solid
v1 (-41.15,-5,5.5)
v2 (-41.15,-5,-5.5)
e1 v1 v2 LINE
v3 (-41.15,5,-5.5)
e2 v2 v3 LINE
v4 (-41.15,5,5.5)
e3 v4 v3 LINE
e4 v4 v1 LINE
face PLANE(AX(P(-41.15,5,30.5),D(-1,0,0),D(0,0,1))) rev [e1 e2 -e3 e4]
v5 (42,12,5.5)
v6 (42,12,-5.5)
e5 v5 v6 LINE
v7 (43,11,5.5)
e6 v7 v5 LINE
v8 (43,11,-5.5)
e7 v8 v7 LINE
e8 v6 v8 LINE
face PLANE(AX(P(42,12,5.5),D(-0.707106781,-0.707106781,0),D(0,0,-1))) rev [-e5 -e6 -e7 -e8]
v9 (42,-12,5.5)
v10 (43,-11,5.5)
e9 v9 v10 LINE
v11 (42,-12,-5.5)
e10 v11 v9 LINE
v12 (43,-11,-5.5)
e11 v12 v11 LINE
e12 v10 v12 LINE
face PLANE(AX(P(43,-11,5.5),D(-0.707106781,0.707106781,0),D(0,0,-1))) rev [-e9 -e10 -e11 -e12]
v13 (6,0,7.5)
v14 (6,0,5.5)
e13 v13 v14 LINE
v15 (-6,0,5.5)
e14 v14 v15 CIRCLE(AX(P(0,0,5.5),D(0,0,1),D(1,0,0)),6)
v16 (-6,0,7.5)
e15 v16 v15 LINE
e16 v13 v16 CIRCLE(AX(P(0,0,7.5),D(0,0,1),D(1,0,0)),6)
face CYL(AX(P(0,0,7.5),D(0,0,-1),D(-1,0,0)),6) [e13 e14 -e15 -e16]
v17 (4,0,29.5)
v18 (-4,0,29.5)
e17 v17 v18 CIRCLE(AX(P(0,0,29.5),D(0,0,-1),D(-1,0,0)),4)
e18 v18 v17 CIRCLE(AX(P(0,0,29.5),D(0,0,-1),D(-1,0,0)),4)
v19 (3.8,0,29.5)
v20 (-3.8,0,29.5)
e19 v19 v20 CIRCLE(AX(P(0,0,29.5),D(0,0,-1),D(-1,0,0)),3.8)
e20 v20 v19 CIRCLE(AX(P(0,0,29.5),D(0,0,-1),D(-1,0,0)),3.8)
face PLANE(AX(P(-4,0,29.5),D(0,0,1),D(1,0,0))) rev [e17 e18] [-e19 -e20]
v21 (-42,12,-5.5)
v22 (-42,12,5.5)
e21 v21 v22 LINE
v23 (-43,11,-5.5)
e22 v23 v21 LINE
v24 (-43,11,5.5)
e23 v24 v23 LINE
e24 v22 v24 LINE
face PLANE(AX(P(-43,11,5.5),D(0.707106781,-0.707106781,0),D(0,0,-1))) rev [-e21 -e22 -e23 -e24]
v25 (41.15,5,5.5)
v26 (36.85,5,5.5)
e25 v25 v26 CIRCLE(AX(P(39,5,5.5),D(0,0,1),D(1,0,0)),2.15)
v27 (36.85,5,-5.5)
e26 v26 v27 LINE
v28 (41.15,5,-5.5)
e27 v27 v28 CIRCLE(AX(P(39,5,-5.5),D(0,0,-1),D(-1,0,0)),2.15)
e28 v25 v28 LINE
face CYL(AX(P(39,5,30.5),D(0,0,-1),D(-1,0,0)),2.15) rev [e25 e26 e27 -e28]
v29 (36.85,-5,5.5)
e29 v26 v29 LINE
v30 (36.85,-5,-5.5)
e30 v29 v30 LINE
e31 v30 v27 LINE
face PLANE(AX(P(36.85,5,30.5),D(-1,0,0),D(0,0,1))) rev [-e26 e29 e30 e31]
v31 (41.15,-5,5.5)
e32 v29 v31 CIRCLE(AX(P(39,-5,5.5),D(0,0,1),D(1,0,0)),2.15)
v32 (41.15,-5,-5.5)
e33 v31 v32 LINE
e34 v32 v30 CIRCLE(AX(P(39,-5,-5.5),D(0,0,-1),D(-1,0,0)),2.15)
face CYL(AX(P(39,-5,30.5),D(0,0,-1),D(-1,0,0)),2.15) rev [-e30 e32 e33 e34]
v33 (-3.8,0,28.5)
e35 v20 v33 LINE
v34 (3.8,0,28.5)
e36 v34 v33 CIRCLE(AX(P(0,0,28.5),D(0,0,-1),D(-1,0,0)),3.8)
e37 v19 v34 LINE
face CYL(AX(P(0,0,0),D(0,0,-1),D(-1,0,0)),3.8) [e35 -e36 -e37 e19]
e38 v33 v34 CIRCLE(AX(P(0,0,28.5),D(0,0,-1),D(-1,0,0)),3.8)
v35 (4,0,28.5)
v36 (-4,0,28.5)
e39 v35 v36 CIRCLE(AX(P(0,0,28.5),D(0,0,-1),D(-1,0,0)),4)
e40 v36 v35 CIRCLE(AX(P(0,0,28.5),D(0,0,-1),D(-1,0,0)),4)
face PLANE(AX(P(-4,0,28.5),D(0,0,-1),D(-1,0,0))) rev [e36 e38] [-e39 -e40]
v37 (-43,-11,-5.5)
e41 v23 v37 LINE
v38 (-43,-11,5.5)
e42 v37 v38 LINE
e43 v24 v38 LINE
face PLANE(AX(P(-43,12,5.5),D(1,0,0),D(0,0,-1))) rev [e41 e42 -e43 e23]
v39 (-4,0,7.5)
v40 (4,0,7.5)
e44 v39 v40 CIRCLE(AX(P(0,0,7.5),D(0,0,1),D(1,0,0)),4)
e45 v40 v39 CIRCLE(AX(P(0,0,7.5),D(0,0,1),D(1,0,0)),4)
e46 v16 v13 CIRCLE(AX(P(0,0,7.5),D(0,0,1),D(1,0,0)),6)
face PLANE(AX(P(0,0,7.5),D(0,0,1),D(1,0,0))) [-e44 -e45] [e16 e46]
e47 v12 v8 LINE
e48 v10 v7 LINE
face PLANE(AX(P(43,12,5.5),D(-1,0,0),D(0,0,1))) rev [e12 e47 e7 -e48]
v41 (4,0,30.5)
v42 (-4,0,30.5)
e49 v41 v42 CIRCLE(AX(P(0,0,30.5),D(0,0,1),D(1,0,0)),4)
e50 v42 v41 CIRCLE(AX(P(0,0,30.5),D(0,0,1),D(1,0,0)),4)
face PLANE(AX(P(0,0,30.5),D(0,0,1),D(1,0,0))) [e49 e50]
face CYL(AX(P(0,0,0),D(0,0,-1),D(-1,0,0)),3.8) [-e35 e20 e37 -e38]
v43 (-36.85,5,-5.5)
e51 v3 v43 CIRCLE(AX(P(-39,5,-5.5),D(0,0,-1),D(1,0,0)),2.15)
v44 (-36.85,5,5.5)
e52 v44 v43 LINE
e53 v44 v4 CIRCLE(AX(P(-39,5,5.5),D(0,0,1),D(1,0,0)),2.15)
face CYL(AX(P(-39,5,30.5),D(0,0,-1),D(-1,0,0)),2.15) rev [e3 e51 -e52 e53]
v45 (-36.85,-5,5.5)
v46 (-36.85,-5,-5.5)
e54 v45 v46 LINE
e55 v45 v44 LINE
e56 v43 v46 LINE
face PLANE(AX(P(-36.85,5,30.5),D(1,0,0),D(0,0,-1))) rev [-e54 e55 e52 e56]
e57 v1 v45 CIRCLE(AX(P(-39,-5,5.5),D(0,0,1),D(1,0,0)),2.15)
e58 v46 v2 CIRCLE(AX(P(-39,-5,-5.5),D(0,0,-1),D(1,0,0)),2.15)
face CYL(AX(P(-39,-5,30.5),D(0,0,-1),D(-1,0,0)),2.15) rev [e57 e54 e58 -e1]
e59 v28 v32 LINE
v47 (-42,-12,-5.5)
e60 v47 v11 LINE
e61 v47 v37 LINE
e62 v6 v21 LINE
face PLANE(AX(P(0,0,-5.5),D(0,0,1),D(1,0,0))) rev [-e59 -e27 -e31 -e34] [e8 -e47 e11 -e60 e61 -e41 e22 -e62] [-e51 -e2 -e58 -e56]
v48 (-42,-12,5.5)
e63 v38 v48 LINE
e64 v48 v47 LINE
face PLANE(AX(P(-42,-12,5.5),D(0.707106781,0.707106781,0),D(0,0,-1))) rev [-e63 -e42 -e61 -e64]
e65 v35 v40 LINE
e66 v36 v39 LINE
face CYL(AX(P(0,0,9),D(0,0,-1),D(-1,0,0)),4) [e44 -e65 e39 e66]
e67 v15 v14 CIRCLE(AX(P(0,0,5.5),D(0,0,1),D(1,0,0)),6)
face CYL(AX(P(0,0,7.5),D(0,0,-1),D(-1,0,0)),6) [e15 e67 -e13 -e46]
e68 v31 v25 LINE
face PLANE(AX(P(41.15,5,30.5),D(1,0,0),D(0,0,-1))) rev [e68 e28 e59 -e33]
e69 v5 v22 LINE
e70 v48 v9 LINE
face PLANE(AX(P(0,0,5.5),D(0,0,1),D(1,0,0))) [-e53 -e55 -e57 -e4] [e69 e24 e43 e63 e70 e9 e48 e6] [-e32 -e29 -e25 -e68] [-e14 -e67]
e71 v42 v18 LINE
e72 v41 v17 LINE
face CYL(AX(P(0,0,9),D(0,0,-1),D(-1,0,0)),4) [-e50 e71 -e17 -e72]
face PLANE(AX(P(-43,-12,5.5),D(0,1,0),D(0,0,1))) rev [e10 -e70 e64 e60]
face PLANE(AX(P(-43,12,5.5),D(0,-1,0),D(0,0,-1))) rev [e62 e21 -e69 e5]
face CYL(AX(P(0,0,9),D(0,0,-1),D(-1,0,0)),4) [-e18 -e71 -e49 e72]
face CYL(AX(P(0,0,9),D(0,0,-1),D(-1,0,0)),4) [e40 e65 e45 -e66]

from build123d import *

# Parameters (mm, degrees)
SKETCH_1_W          = 86
SKETCH_1_H          = 24
EXTRUDE_1_DEPTH     = 5.5
SKETCH_2_R          = 4
EXTRUDE_2_DEPTH     = 3.5
SKETCH_3_R          = 4
EXTRUDE_3_DEPTH     = 21.5
CUT_EXTRUDE_4_DEPTH = 58.349803836
SKETCH_15_R         = 4
CUT_EXTRUDE_5_DEPTH = 9.999
SKETCH_4_W          = 0.2
SKETCH_4_H          = 1
SKETCH_16_R         = 2.9995
EXTRUDE_4_DEPTH     = 8.999
SKETCH_18_R         = 6
EXTRUDE_5_DEPTH     = 2
SKETCH_22_R         = 7.5
EXTRUDE_7_DEPTH     = 11
CHAMFER_1_SIZE      = 1


with BuildPart() as part:
    # 草图1 → 凸台-拉伸1 (new, symmetric)
    with BuildSketch(Plane.XY):
        Rectangle(SKETCH_1_W, SKETCH_1_H)
    extrude(amount=EXTRUDE_1_DEPTH, both=True)

    # 草图2 → 凸台-拉伸2 (add)
    with BuildSketch(Plane.XY.offset(5.5)):
        Circle(SKETCH_2_R)
    extrude(amount=EXTRUDE_2_DEPTH)

    # 草图3 → 凸台-拉伸3 (add)
    with BuildSketch(Plane.XY.offset(9)):
        Circle(SKETCH_3_R)
    extrude(amount=EXTRUDE_3_DEPTH)

    # 草图14 → 切除-拉伸4 (cut, through all)
    with BuildSketch(Plane(origin=(0, 0, -5.5), x_dir=(-1, 0, 0), z_dir=(0, 0, -1))):
        with BuildLine():
            Line((-36.85, 5), (-36.85, -5))
            ThreePointArc((-36.85, -5), (-39, -7.15), (-41.15, -5))
            Line((-41.15, -5), (-41.15, 5))
            ThreePointArc((-41.15, 5), (-39, 7.15), (-36.85, 5))
        make_face()
        with BuildLine():
            Line((36.85, 5), (36.85, -5))
            ThreePointArc((36.85, -5), (39, -7.15), (41.15, -5))
            Line((41.15, -5), (41.15, 5))
            ThreePointArc((41.15, 5), (39, 7.15), (36.85, 5))
        make_face()
    extrude(amount=-CUT_EXTRUDE_4_DEPTH, mode=Mode.SUBTRACT)

    # 草图15 → 切除-拉伸5 (cut)
    with BuildSketch(Plane(origin=(0, 0, -5.5), x_dir=(-1, 0, 0), z_dir=(0, 0, -1))):
        with Locations(Location((0, 0, 0), (0, 0, 180))):
            Circle(SKETCH_15_R)
    extrude(amount=-CUT_EXTRUDE_5_DEPTH, mode=Mode.SUBTRACT)

    # 草图4 → 切除-旋转1 (revolve, cut)
    with BuildSketch(Plane(origin=(0, 0, 0), x_dir=(1, 0, 0), z_dir=(0, 1, 0))):
        with Locations((-3.9, -29)):
            Rectangle(SKETCH_4_W, SKETCH_4_H)
    revolve(axis=Axis((0, 0, 0), (0, 0, 1)), mode=Mode.SUBTRACT)

    # 草图16 → 凸台-拉伸4 (add)
    with BuildSketch(Plane(origin=(0, 0, 4.499), x_dir=(-1, 0, 0), z_dir=(0, 0, -1))):
        Circle(SKETCH_16_R)
    extrude(amount=EXTRUDE_4_DEPTH)

    # 草图18 → 凸台-拉伸5 (add)
    with BuildSketch(Plane.XY.offset(5.5)):
        Circle(SKETCH_18_R)
    extrude(amount=EXTRUDE_5_DEPTH)

    # 草图22 → 凸台-拉伸7 (add)
    with BuildSketch(Plane(origin=(0, 0, -5.5), x_dir=(-1, 0, 0), z_dir=(0, 0, -1))):
        Circle(SKETCH_22_R)
    extrude(amount=-EXTRUDE_7_DEPTH)

    # 倒角1
    chamfer_1_edges = [part.edges().sort_by_distance(p)[0] for p in [
        (43, -12, 0),
        (-43, -12, 0),
        (-43, 12, 0),
        (43, 12, 0),
    ]]
    chamfer(chamfer_1_edges, length=CHAMFER_1_SIZE)


solid = part.part
